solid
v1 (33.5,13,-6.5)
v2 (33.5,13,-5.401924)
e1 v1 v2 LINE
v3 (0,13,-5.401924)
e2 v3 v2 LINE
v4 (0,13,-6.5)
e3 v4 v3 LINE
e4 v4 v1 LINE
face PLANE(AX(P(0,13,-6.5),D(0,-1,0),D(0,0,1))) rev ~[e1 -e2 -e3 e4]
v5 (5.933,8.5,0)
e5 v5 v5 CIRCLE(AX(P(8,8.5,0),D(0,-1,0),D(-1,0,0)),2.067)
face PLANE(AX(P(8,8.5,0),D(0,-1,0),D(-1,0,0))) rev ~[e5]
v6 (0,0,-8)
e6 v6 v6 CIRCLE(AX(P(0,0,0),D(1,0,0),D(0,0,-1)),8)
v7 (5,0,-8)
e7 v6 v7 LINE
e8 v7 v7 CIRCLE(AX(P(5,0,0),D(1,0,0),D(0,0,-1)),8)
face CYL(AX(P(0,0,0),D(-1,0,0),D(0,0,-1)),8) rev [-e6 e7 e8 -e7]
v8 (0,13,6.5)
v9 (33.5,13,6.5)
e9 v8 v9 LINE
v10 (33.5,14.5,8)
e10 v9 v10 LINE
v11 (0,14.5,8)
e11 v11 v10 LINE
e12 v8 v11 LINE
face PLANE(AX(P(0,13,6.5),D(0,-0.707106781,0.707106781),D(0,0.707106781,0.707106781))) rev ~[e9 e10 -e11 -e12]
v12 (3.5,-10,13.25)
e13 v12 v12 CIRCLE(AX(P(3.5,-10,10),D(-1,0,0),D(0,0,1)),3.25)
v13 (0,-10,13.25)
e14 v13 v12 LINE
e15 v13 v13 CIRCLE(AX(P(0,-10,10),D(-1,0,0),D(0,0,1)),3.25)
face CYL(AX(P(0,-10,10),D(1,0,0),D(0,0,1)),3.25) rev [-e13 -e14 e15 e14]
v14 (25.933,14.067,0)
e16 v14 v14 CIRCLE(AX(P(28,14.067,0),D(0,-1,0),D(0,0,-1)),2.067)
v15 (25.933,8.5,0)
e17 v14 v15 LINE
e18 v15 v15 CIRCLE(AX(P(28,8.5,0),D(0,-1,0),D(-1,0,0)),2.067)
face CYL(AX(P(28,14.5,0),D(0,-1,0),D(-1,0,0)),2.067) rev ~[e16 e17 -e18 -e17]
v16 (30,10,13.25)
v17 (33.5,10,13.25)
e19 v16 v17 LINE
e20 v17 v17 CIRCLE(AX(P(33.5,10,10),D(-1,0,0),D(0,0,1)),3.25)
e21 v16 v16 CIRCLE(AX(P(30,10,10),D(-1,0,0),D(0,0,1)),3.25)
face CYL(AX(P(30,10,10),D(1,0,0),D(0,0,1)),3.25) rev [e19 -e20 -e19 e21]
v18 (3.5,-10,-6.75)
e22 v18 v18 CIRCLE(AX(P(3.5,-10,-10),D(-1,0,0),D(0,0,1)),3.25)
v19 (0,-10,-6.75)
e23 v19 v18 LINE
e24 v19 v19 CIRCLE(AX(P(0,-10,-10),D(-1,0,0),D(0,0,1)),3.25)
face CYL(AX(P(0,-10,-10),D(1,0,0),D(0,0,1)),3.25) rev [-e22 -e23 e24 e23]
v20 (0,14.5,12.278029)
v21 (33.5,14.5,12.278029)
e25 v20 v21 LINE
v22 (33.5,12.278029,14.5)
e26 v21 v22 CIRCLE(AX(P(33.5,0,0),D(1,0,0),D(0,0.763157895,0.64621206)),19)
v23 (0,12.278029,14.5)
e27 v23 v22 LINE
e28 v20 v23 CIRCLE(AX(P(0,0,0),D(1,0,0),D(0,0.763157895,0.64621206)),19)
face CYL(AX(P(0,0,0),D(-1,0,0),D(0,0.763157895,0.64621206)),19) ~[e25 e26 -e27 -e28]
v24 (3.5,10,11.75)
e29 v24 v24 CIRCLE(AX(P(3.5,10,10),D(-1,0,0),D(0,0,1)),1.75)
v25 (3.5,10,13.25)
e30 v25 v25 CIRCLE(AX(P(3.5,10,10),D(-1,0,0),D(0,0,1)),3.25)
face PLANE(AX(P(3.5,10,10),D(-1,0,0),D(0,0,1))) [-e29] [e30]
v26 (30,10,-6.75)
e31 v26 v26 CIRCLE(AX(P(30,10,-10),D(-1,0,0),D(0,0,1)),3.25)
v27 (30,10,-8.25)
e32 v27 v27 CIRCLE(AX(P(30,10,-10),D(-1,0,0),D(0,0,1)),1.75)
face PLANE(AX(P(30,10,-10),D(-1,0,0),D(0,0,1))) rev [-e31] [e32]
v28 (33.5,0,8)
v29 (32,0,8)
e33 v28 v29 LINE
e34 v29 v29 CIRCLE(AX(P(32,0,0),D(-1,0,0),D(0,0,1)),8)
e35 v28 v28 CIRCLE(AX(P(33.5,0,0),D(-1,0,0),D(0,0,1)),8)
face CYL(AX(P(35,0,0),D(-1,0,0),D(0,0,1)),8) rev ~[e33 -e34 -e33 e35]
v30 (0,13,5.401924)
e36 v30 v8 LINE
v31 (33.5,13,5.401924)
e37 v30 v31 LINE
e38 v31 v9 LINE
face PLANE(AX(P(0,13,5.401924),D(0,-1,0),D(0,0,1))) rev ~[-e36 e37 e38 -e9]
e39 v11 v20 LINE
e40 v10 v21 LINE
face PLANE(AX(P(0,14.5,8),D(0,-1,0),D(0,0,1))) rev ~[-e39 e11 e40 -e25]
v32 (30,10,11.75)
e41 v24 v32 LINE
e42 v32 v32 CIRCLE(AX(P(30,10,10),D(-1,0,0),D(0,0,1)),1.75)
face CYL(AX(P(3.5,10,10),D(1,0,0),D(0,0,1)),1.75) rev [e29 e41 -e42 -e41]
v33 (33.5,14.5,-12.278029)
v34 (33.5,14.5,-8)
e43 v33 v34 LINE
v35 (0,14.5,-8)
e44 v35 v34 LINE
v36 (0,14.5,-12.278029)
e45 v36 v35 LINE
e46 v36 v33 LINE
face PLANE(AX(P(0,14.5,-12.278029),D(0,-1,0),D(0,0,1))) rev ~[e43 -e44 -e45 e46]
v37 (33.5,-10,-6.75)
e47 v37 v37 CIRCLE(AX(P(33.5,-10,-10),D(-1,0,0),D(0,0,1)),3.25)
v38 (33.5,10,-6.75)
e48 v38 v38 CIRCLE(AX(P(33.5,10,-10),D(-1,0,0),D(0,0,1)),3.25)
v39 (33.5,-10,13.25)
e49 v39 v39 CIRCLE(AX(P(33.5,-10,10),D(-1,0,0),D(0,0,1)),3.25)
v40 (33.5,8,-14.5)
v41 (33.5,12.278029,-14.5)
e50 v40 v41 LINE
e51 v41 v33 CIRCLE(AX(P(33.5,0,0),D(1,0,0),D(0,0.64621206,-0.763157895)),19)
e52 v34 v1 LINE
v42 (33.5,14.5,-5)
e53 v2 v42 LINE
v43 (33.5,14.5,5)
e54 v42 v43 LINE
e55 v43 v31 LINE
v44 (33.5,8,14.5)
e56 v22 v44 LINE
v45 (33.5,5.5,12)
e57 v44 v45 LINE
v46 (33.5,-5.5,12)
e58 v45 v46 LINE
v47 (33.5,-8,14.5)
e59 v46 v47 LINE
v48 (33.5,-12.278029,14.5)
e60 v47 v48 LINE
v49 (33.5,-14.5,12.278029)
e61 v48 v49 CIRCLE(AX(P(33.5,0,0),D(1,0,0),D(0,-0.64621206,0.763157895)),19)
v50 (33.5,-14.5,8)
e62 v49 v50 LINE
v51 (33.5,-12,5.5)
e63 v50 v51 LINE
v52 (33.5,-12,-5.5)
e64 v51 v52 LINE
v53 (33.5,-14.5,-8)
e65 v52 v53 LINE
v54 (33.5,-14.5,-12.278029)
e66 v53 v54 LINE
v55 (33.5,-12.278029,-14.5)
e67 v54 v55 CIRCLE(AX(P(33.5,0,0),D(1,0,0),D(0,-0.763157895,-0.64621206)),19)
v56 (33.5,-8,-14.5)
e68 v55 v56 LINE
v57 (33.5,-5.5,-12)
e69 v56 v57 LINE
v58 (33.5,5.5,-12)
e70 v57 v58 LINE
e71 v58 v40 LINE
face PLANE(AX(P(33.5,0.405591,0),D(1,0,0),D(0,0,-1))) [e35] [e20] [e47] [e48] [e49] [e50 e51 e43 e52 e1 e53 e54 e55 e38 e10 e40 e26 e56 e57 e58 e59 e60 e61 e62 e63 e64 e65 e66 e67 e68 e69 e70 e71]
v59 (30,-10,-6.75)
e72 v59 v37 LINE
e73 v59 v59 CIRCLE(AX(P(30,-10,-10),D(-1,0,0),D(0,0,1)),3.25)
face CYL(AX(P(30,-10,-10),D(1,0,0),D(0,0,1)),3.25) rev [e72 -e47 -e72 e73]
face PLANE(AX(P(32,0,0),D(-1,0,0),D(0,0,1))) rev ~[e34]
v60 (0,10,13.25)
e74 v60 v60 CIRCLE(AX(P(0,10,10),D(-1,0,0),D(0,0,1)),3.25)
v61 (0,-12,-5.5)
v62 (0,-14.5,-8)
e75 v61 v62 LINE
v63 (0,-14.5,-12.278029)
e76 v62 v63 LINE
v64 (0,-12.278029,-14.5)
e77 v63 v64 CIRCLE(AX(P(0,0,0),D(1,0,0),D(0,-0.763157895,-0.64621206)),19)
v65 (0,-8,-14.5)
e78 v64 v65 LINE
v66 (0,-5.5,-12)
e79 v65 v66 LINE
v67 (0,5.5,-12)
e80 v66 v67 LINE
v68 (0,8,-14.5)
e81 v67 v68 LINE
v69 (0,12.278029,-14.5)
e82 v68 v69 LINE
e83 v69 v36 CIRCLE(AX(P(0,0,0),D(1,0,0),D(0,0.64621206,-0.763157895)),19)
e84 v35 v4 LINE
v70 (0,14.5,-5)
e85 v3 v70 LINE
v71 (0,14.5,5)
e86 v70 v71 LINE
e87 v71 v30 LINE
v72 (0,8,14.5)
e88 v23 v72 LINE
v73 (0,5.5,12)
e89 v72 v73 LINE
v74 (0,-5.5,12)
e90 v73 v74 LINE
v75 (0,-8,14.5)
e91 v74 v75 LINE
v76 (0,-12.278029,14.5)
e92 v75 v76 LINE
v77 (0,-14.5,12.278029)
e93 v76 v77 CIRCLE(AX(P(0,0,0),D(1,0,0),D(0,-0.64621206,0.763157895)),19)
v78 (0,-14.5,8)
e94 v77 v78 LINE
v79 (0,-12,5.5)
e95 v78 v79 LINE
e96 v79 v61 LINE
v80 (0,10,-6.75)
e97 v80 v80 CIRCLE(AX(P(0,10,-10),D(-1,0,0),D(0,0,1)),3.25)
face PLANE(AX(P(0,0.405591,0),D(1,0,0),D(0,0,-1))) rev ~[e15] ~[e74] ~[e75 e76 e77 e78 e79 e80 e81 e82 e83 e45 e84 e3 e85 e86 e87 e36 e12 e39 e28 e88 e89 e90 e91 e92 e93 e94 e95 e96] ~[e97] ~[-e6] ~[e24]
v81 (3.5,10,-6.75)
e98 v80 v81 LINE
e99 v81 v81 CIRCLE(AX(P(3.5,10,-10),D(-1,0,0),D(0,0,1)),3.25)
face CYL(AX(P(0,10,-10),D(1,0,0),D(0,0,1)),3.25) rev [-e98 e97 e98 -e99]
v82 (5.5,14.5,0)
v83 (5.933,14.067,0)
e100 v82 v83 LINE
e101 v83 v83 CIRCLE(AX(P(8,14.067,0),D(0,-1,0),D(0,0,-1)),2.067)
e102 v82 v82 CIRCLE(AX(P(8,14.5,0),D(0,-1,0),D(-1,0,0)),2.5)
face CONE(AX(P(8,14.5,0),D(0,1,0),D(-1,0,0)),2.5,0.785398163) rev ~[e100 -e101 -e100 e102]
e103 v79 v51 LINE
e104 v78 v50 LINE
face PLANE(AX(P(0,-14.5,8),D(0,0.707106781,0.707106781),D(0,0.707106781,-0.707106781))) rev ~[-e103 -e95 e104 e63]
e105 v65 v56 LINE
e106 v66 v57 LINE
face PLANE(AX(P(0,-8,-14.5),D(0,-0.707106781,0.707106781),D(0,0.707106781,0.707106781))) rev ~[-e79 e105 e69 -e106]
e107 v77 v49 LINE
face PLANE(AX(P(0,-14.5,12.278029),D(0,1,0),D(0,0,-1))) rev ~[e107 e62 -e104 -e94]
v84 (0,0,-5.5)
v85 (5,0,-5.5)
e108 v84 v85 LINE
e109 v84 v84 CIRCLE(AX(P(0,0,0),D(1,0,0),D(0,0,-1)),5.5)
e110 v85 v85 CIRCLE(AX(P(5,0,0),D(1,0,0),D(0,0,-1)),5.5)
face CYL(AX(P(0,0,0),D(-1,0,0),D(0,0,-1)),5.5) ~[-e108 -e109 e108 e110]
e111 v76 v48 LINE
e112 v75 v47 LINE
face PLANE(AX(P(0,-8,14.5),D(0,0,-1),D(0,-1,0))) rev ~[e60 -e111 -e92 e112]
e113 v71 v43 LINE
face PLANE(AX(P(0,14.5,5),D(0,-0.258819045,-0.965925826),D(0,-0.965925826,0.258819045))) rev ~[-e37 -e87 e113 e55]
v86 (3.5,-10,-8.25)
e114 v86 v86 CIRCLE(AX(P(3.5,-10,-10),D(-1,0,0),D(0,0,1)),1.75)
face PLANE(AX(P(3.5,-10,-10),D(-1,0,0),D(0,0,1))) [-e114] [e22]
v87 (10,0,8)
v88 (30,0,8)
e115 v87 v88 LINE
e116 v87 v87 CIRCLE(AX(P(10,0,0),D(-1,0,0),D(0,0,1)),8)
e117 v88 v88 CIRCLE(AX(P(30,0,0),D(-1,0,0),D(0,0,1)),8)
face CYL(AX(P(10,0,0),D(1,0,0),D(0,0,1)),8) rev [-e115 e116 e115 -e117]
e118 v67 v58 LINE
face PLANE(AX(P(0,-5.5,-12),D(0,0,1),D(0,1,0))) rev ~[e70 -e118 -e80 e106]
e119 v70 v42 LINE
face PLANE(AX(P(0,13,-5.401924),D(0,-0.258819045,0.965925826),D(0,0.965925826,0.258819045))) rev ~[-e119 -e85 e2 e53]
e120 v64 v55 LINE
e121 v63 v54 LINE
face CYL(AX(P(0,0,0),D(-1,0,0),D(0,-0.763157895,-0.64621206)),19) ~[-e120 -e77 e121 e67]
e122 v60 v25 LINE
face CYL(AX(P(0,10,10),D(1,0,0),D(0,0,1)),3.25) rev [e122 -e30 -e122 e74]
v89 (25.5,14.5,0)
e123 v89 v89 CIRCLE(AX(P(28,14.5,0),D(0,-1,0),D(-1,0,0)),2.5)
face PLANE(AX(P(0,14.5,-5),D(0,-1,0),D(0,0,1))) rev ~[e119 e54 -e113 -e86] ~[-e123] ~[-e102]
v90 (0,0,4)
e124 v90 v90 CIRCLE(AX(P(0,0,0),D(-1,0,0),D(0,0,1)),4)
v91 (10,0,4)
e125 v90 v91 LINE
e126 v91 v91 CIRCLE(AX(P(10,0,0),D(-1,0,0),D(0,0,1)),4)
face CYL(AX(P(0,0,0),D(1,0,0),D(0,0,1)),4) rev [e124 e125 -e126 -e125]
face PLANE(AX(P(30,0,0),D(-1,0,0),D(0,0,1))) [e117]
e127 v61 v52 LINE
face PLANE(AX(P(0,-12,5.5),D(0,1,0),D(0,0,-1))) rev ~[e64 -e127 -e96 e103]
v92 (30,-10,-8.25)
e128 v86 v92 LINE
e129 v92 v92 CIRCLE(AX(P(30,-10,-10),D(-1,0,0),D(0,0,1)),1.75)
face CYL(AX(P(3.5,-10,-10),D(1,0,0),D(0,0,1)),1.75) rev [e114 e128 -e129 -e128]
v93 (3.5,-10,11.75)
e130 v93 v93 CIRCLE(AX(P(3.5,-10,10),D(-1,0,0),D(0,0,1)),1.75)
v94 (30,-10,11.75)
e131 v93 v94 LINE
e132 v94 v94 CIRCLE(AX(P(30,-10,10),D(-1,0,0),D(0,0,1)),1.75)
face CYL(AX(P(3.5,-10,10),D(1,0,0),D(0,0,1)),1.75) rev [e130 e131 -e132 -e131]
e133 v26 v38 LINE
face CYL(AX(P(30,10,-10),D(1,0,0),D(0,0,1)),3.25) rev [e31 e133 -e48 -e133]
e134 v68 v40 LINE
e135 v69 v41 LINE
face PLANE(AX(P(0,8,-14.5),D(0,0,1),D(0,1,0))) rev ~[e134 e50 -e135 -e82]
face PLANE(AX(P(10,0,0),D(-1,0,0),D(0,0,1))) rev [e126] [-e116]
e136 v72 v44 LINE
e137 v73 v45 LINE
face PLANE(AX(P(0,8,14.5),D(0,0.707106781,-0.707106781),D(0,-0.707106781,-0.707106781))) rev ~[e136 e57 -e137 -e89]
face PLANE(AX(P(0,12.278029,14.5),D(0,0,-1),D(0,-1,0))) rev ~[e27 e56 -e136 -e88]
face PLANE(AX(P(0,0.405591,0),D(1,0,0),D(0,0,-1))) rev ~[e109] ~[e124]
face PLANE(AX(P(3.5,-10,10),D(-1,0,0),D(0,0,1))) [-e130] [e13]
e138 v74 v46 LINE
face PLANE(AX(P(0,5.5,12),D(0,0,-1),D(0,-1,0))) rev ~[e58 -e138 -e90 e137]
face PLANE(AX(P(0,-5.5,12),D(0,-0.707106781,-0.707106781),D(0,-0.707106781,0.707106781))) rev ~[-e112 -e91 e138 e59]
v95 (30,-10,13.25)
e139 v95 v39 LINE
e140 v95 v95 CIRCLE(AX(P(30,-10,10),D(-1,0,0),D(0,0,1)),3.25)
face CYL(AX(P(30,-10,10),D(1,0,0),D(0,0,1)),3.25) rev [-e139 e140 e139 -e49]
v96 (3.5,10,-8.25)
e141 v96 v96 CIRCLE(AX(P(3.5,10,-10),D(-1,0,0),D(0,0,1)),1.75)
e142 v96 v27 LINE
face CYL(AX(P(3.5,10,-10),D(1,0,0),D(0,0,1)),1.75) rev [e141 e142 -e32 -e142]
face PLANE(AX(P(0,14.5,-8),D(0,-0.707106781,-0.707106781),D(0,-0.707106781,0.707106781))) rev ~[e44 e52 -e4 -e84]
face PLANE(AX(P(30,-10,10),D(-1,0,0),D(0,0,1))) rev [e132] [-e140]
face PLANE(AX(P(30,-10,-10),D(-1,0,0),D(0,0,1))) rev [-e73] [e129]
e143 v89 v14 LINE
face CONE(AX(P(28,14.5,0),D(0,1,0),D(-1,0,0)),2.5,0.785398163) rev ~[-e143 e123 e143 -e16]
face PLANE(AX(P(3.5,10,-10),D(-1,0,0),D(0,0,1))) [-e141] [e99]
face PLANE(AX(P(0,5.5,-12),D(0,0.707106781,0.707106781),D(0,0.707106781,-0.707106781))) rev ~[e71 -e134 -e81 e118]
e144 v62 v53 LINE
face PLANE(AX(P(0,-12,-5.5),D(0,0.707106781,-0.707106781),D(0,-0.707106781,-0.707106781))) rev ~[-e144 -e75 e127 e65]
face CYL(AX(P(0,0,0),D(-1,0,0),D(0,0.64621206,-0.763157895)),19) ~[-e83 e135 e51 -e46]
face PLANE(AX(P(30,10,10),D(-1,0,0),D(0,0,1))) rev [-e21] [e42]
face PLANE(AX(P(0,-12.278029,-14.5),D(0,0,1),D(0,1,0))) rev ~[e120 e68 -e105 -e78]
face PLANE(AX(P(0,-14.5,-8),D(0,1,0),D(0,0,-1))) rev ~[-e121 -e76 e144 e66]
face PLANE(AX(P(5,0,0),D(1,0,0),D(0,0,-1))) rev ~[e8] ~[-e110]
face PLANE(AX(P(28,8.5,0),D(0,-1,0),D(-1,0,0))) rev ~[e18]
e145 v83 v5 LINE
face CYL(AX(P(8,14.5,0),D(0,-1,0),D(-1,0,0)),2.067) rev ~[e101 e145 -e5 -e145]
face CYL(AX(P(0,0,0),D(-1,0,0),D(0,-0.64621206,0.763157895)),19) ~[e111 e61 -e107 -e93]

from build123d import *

# Parameters (mm, degrees)
BOSS_EXTRUDE1_DEPTH  = 33.5
HOLE1_D              = 16
HOLE1_DEPTH          = 1.5
SKETCH4_R            = 8
SKETCH4_R_2          = 5.5
CUT_EXTRUDE1_DEPTH   = 5
HOLE2_D              = 4.134
HOLE2_DEPTH          = 6
HOLE2_CSINK_D        = 5
HOLE2_CSINK_ANGLE    = 90
LPATTERN1_COUNT      = 2
LPATTERN1_PITCH      = 20
LPATTERN2_COUNT      = 2
LPATTERN2_PITCH      = 20
LPATTERN2_COUNT_DIR2 = 2
LPATTERN2_PITCH_DIR2 = 20


with BuildPart() as part:
    # Sketch1 → Boss-Extrude1 (new body)
    with BuildSketch(Plane(origin=(0, 0, 0), x_dir=(0, 0, -1), z_dir=(1, 0, 0))):
        with BuildLine():
            Line((-12.278029158, -14.5), (-8, -14.5))
            Line((-8, -14.5), (-5.5, -12))
            Line((-5.5, -12), (5.5, -12))
            Line((5.5, -12), (8, -14.5))
            Line((8, -14.5), (12.278029158, -14.5))
            ThreePointArc((12.278029158, -14.5), (13.435028843, -13.435028843), (14.5, -12.278029158))
            Line((14.5, -12.278029158), (14.5, -8))
            Line((14.5, -8), (12, -5.5))
            Line((12, -5.5), (12, 5.5))
            Line((12, 5.5), (14.5, 8))
            Line((14.5, 8), (14.5, 12.278029158))
            ThreePointArc((14.5, 12.278029158), (13.435028843, 13.435028843), (12.278029158, 14.5))
            Line((12.278029158, 14.5), (8, 14.5))
            Line((8, 14.5), (6.5, 13))
            Line((6.5, 13), (5.401923789, 13))
            Line((5.401923789, 13), (5, 14.5))
            Line((5, 14.5), (-5, 14.5))
            Line((-5, 14.5), (-5.401923789, 13))
            Line((-5.401923789, 13), (-6.5, 13))
            Line((-6.5, 13), (-8, 14.5))
            Line((-8, 14.5), (-12.278029158, 14.5))
            ThreePointArc((-12.278029158, 14.5), (-13.435028843, 13.435028843), (-14.5, 12.278029158))
            Line((-14.5, 12.278029158), (-14.5, 8))
            Line((-14.5, 8), (-12, 5.5))
            Line((-12, 5.5), (-12, -5.5))
            Line((-12, -5.5), (-14.5, -8))
            Line((-14.5, -8), (-14.5, -12.278029158))
            ThreePointArc((-14.5, -12.278029158), (-13.435028843, -13.435028843), (-12.278029158, -14.5))
        make_face()
    extrude(amount=BOSS_EXTRUDE1_DEPTH)

    # Hole1
    with Locations(Plane(origin=(33.5, 0, 0), x_dir=(0, 0, -1), z_dir=(1, 0, 0))):
        with Locations((0, 0)):
            Hole(HOLE1_D / 2, depth=HOLE1_DEPTH)

    # Sketch4 → Cut-Extrude1 (cut)
    with BuildSketch(Plane(origin=(0, 0, 0), x_dir=(0, 0, -1), z_dir=(1, 0, 0))):
        Circle(SKETCH4_R)
        Circle(SKETCH4_R_2, mode=Mode.SUBTRACT)
    extrude(amount=CUT_EXTRUDE1_DEPTH, mode=Mode.SUBTRACT)

    # Sketch5 → Cut-Revolve1 (revolve, cut)
    with BuildSketch(Plane.XY, mode=Mode.PRIVATE) as cut_revolve1_sk:
        Polygon((0, 0), (0, 4), (10, 4), (10, 8), (30, 8), (30, 0), align=None)
    revolve(cut_revolve1_sk.sketch.rotate(Axis((30, 0, 0), (-1, 0, 0)), 270), axis=Axis((30, 0, 0), (-1, 0, 0)), mode=Mode.SUBTRACT)

    # Hole2
    with Locations(Plane(origin=(0, 14.5, 0), x_dir=(1, 0, 0), z_dir=(0, 1, 0))):
        with Locations((8, 0)):
            hole2 = CounterSinkHole(HOLE2_D / 2, HOLE2_CSINK_D / 2, depth=HOLE2_DEPTH, counter_sink_angle=HOLE2_CSINK_ANGLE)

    # LPattern1: Hole2 ×2
    with Locations(*[(i * LPATTERN1_PITCH, 0, 0) for i in range(1, LPATTERN1_COUNT)]):
        add(hole2, mode=Mode.SUBTRACT)

    # Sketch9 → Cut-Revolve2 (revolve, cut)
    with BuildSketch(Plane.XY.offset(10), mode=Mode.PRIVATE) as cut_revolve2_sk:
        Polygon((0, 10), (0, 13.25), (3.5, 13.25), (3.5, 11.75), (30, 11.75), (30, 13.25), (33.5, 13.25), (33.5, 10), align=None)
    cut_revolve2 = revolve(cut_revolve2_sk.sketch.rotate(Axis((33.5, 10, 10), (-1, 0, 0)), 270), axis=Axis((33.5, 10, 10), (-1, 0, 0)), mode=Mode.SUBTRACT)

    # LPattern2: Cut-Revolve2 2 × 2
    with Locations(*[(0, -j * LPATTERN2_PITCH_DIR2, -i * LPATTERN2_PITCH) for i in range(LPATTERN2_COUNT) for j in range(LPATTERN2_COUNT_DIR2) if (i, j) != (0, 0)]):
        add(cut_revolve2, mode=Mode.SUBTRACT)


solid = part.part
